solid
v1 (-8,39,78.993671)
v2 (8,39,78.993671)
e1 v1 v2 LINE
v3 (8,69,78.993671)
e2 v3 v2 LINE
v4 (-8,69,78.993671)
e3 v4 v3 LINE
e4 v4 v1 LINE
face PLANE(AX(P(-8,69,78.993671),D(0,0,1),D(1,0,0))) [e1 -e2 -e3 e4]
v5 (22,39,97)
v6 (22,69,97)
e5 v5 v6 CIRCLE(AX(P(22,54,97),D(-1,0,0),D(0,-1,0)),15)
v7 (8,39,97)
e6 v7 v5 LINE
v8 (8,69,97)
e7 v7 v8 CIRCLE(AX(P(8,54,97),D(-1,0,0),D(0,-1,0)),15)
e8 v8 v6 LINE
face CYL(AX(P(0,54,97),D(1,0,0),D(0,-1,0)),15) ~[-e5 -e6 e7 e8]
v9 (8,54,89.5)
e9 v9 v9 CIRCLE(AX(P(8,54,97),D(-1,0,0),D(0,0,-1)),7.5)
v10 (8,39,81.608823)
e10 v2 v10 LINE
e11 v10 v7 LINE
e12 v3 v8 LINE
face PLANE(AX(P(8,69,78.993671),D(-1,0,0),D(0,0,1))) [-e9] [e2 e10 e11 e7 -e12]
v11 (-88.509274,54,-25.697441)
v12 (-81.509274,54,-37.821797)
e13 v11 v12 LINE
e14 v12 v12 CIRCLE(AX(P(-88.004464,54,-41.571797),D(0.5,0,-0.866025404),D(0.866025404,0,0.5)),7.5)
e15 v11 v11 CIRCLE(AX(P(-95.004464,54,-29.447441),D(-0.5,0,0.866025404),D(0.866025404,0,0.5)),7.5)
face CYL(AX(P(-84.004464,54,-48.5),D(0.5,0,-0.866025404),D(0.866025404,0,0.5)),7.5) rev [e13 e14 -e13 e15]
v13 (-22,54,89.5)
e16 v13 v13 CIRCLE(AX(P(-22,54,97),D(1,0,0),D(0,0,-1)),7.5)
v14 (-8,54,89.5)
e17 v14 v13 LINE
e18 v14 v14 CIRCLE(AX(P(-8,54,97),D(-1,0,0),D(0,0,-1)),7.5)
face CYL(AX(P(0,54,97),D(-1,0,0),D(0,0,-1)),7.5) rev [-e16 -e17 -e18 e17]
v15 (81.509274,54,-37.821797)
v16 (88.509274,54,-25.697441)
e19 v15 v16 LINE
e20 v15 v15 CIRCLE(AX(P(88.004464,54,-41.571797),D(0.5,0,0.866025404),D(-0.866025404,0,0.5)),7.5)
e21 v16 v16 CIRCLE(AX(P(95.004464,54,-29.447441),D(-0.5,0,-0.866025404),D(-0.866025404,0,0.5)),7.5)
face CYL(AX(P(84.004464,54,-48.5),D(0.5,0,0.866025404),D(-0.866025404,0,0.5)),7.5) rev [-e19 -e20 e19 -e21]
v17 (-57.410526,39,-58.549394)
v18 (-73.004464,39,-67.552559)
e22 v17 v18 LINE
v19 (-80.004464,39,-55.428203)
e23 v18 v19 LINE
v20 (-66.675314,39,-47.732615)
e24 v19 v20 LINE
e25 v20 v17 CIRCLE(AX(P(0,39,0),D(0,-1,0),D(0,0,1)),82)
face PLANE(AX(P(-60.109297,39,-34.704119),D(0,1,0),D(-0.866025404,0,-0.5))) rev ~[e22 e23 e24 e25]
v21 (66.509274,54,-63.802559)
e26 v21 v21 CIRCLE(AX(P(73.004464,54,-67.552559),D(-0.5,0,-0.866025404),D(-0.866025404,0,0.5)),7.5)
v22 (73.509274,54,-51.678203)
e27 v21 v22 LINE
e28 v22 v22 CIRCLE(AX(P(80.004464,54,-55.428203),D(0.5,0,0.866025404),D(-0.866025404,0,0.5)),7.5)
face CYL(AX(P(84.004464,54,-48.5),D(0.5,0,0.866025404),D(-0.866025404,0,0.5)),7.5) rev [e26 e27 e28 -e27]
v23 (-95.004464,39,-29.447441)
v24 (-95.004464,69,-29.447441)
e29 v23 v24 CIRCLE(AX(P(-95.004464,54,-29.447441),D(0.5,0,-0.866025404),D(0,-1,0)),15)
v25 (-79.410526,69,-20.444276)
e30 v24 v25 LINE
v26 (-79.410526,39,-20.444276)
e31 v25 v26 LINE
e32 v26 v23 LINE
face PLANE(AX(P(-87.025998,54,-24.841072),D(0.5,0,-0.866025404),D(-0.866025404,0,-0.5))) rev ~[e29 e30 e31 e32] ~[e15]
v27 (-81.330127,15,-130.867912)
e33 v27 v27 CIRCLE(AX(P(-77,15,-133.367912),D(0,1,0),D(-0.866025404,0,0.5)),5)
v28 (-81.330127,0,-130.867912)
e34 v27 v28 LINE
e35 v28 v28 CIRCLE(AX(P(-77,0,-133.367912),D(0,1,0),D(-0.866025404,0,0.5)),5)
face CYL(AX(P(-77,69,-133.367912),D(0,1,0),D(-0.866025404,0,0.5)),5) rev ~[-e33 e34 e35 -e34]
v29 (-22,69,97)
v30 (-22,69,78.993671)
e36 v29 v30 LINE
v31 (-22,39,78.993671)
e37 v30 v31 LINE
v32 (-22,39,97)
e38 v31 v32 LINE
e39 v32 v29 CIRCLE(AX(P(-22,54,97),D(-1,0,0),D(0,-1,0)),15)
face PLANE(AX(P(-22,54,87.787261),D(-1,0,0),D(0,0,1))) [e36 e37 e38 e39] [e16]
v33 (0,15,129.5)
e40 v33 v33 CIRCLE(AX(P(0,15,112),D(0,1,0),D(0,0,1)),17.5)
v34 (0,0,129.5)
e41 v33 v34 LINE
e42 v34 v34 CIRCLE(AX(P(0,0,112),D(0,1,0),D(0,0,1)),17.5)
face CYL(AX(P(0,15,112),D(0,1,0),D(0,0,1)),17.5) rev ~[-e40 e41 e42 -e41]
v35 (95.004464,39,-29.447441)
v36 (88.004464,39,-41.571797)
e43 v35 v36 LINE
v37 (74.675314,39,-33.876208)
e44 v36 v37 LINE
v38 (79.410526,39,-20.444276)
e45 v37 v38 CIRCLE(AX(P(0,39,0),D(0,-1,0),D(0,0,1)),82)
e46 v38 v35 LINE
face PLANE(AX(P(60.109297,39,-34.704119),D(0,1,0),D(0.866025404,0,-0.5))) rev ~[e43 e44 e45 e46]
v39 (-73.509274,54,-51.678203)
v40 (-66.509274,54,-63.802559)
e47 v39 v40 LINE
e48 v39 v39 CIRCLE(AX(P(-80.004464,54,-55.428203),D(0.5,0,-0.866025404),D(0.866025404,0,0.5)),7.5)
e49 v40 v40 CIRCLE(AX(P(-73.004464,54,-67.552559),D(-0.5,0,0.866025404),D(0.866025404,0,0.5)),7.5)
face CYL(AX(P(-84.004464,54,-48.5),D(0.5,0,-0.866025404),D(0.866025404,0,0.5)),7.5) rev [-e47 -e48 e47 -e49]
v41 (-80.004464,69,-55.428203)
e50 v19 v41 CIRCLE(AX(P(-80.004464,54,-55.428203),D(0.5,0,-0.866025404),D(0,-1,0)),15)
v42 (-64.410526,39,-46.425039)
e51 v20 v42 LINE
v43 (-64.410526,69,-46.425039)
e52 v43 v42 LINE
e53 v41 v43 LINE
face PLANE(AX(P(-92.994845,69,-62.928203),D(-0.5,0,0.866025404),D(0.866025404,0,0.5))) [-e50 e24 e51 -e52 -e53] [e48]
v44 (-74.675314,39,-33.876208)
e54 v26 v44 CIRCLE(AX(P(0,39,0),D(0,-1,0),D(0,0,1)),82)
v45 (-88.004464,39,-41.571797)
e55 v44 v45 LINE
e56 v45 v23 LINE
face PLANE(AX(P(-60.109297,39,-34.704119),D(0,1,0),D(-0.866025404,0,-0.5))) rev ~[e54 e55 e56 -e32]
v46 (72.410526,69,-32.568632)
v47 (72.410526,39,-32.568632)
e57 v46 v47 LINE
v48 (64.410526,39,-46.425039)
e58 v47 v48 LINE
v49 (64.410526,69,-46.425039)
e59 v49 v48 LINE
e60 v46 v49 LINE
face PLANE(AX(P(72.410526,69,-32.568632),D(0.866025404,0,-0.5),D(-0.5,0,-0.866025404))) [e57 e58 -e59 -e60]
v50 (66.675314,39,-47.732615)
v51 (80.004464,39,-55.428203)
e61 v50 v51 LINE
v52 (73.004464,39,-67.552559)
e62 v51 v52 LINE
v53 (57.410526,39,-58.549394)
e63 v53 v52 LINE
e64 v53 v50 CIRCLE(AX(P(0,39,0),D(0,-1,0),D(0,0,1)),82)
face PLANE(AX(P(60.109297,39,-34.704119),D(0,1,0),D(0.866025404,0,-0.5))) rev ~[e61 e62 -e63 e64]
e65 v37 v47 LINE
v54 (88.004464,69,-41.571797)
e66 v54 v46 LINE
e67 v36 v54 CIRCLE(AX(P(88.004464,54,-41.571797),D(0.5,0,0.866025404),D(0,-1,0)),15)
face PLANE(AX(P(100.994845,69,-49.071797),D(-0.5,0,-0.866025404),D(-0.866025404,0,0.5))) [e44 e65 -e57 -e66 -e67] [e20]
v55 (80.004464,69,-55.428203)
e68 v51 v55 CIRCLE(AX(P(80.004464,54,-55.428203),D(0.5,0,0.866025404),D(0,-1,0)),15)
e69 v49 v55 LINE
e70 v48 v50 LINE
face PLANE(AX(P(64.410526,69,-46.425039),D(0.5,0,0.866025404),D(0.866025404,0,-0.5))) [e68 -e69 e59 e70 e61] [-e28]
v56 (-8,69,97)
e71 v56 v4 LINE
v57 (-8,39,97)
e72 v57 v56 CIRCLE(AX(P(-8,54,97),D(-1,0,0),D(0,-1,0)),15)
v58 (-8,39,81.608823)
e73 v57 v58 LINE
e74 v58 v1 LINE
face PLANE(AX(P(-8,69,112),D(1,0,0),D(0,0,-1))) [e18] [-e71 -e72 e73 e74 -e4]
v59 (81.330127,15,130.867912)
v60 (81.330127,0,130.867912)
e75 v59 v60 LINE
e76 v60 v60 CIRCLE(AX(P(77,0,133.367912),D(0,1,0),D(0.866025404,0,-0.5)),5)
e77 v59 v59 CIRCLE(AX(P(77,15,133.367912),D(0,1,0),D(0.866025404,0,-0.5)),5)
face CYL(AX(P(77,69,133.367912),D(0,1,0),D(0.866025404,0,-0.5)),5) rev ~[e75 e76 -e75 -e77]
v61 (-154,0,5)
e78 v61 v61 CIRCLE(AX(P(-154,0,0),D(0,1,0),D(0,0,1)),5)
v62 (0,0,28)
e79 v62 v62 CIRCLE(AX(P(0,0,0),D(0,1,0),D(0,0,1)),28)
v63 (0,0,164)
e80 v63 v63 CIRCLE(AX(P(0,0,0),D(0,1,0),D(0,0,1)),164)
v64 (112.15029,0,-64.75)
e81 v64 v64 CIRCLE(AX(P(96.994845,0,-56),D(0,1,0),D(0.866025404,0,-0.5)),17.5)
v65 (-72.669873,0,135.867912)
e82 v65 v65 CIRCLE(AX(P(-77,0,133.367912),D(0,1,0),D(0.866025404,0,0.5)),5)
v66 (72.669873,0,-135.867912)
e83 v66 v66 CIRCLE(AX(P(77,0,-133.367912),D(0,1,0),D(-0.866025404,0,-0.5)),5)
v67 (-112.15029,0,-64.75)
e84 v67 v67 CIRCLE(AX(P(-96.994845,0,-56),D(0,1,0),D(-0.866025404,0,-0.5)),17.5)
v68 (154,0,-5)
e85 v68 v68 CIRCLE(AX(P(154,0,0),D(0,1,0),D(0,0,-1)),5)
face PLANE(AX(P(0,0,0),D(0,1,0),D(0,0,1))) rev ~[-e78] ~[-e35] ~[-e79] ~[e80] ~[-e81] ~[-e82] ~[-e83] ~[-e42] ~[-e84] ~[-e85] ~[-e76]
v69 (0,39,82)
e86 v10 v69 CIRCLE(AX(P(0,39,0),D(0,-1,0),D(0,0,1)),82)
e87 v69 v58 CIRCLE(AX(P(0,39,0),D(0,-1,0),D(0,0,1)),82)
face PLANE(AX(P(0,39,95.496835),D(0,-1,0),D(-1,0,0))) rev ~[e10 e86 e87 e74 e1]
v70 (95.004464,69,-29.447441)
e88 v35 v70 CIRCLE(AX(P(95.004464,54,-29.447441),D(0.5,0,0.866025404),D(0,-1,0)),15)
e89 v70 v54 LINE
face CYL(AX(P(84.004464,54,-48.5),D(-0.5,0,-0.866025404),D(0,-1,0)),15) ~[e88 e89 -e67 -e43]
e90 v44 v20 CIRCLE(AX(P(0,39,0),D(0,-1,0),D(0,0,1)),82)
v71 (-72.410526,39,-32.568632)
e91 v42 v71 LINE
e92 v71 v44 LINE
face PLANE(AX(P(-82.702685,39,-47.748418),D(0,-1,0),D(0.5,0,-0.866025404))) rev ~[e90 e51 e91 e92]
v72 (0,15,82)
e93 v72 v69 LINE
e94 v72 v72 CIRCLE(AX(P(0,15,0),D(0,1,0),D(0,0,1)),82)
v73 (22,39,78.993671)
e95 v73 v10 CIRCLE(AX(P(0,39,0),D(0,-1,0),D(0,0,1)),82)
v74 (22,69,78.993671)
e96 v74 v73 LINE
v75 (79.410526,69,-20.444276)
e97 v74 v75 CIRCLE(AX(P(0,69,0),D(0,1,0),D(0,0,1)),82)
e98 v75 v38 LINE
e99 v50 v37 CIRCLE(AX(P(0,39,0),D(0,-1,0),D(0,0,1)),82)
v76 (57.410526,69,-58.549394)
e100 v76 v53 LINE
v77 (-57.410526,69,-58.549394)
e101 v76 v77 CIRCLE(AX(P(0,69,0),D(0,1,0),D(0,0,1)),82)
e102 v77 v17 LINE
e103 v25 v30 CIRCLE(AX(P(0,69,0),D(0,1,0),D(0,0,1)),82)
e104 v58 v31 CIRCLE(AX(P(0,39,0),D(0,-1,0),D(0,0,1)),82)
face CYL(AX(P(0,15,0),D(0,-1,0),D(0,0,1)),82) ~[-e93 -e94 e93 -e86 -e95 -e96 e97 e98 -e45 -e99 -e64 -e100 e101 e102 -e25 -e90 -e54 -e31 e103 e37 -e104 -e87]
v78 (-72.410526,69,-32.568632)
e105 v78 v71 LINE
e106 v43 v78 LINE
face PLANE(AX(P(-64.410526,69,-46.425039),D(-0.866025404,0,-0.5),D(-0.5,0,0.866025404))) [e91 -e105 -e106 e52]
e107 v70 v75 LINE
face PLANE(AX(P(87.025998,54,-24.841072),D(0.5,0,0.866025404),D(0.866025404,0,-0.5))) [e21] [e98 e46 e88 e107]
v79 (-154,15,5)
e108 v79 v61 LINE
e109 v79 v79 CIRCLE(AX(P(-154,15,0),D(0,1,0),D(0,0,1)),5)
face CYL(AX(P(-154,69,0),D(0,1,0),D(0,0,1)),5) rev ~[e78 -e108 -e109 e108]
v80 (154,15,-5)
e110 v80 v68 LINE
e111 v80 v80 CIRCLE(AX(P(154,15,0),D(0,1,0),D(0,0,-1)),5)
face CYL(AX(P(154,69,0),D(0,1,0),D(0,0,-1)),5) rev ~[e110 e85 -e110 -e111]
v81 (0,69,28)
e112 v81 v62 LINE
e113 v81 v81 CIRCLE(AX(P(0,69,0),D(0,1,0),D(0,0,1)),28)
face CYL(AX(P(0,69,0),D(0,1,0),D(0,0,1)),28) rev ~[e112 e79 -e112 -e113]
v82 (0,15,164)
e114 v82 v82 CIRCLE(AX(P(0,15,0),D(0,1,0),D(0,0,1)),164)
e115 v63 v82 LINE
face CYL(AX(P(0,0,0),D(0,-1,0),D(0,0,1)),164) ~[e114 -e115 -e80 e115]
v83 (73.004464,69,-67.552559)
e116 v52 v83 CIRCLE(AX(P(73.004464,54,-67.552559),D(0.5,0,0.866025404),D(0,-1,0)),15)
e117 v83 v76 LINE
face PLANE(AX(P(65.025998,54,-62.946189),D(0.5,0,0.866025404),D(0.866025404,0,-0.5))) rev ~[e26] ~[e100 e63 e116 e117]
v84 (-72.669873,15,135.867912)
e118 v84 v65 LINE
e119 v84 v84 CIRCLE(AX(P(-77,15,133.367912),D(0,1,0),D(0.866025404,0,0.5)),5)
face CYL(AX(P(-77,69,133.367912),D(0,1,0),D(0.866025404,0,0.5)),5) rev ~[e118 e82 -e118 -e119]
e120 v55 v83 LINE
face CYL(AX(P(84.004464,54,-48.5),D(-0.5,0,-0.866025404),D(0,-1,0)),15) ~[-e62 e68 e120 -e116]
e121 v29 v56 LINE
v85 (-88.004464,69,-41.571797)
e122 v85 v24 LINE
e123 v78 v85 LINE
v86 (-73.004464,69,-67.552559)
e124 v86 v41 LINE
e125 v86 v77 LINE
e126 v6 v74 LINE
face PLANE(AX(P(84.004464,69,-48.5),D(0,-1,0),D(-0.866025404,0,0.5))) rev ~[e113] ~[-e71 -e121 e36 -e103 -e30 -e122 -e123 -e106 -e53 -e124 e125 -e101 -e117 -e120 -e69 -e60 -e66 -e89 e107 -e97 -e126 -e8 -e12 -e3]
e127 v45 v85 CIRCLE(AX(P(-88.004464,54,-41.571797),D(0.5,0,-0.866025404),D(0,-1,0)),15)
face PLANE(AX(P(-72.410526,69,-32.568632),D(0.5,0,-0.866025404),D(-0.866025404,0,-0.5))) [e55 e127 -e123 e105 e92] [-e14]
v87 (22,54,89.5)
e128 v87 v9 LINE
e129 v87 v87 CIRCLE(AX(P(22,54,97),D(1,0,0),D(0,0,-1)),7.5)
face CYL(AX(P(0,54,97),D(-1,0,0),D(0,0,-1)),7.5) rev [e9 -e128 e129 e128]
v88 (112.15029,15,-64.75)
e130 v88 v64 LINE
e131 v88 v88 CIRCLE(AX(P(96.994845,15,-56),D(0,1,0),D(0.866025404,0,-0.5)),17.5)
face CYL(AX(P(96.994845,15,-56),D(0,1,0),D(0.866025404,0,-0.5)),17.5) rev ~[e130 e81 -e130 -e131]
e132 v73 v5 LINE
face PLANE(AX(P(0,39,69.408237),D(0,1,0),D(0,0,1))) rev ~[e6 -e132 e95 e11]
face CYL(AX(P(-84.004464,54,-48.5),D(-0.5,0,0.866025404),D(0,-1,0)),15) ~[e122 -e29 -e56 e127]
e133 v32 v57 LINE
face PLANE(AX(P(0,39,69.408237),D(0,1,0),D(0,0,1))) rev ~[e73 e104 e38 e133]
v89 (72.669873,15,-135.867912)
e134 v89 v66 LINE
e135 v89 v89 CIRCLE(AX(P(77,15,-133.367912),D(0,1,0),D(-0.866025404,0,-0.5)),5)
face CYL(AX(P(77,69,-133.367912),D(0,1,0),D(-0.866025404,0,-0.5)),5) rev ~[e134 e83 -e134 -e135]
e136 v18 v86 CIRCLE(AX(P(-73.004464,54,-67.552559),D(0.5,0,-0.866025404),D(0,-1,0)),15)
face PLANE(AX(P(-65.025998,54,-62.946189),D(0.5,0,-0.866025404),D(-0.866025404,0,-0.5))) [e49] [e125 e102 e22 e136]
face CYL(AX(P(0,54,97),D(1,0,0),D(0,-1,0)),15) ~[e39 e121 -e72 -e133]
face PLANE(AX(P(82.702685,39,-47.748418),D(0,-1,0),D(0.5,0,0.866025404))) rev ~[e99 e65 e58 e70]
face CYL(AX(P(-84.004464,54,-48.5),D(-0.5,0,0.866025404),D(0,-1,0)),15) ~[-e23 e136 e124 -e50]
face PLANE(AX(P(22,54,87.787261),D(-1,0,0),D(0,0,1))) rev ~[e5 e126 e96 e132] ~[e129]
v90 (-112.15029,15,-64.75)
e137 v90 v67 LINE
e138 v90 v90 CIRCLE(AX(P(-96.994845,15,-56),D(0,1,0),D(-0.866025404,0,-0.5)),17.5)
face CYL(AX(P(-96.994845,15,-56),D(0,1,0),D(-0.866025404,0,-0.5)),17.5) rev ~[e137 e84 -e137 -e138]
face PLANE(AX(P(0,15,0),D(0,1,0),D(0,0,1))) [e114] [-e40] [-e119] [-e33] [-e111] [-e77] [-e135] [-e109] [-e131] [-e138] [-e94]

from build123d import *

# Parameters (mm, degrees)
BASE_DISC_SKETCH_328_R            = 164
BASE_DISC_328X15_DEPTH            = 15
HUB_SKETCH_164_R                  = 82
HUB_164X54_DEPTH                  = 54
CENTRE_BORE_SKETCH_56_R           = 28
CENTRE_BORE_56_DEPTH              = 242.97727166
CLEVIS_LUG_PROFILE_SKETCH_R       = 7.5
CLEVIS_LUG_DEPTH                  = 22
CLEVIS_SLOT_30_DEPTH              = 30
CLEVIS_LUG_PATTERN_3X_COUNT       = 3
LARGE_HOLE_SKETCH_35_R            = 17.5
LARGE_HOLE_35_DEPTH               = 239.134415824
LARGE_HOLE_PATTERN_3X_35_COUNT    = 3
MOUNTING_HOLE_SKETCH_10_R         = 5
MOUNTING_HOLE_10_DEPTH            = 242.97727166
MOUNTING_HOLE_PATTERN_6X_10_COUNT = 6


with BuildPart() as part:
    # Base Disc Sketch Ø328 → Base Disc Ø328x15 (new body)
    with BuildSketch(Plane(origin=(0, 0, 0), x_dir=(1, 0, 0), z_dir=(0, 1, 0))):
        with Locations(Location((0, 0, 0), (0, 0, 270))):
            Circle(BASE_DISC_SKETCH_328_R)
    extrude(amount=BASE_DISC_328X15_DEPTH)

    # Hub Sketch Ø164 → Hub Ø164x54 (add)
    with BuildSketch(Plane(origin=(0, 15, 0), x_dir=(1, 0, 0), z_dir=(0, 1, 0))):
        with Locations(Location((0, 0, 0), (0, 0, 270))):
            Circle(HUB_SKETCH_164_R)
    extrude(amount=HUB_164X54_DEPTH)

    # Centre Bore Sketch Ø56 → Centre Bore Ø56 (cut, through all)
    with BuildSketch(Plane(origin=(0, 69, 0), x_dir=(1, 0, 0), z_dir=(0, 1, 0))):
        with Locations(Location((0, 0, 0), (0, 0, 270))):
            Circle(CENTRE_BORE_SKETCH_56_R)
    extrude(amount=-CENTRE_BORE_56_DEPTH, mode=Mode.SUBTRACT)

    # Clevis Lug Profile Sketch → Clevis Lug (add, symmetric)
    with BuildSketch(Plane(origin=(0, 0, 0), x_dir=(0, 0, -1), z_dir=(1, 0, 0))):
        with BuildLine():
            Line((-97, 69), (-69.408237338, 69))
            Line((-69.408237338, 69), (-69.408237338, 39))
            Line((-69.408237338, 39), (-97, 39))
            ThreePointArc((-97, 39), (-112, 54), (-97, 69))
        make_face()
        with Locations((-97, 54)):
            Circle(CLEVIS_LUG_PROFILE_SKETCH_R, mode=Mode.SUBTRACT)
    clevis_lug = extrude(amount=CLEVIS_LUG_DEPTH, both=True)

    # Clevis Slot Profile Sketch → Clevis Slot 30 (cut)
    with BuildSketch(Plane(origin=(0, 69, 0), x_dir=(1, 0, 0), z_dir=(0, 1, 0))):
        Polygon((0, -112), (-8, -112), (-8, -78.993670633), (8, -78.993670633), (8, -112), align=None)
    clevis_slot_30 = extrude(amount=-CLEVIS_SLOT_30_DEPTH, mode=Mode.SUBTRACT)

    # Clevis Lug Pattern 3x: Clevis Lug, Clevis Slot 30 ×3 about axis
    clevis_lug_pattern_3x_axis = Axis((0, 0, 0), (0, 1, 0))
    add([clevis_lug.rotate(clevis_lug_pattern_3x_axis, i * 360 / CLEVIS_LUG_PATTERN_3X_COUNT) for i in range(1, CLEVIS_LUG_PATTERN_3X_COUNT)])
    add([clevis_slot_30.rotate(clevis_lug_pattern_3x_axis, i * 360 / CLEVIS_LUG_PATTERN_3X_COUNT) for i in range(1, CLEVIS_LUG_PATTERN_3X_COUNT)], mode=Mode.SUBTRACT)

    # Large Hole Sketch Ø35 → Large Hole Ø35 (cut, through all)
    with BuildSketch(Plane(origin=(0, 15, 0), x_dir=(1, 0, 0), z_dir=(0, 1, 0))):
        with Locations(Location((0, -112, 0), (0, 0, 270))):
            Circle(LARGE_HOLE_SKETCH_35_R)
    large_hole_35 = extrude(amount=-LARGE_HOLE_35_DEPTH, mode=Mode.SUBTRACT)

    # Large Hole Pattern 3xØ35: Large Hole Ø35 ×3 about axis
    large_hole_pattern_3x_35_axis = Axis((0, 0, 0), (0, 1, 0))
    for i in range(1, LARGE_HOLE_PATTERN_3X_35_COUNT):
        add(large_hole_35.rotate(large_hole_pattern_3x_35_axis, i * 360 / LARGE_HOLE_PATTERN_3X_35_COUNT), mode=Mode.SUBTRACT)

    # Mounting Hole Sketch Ø10 → Mounting Hole Ø10 (cut, through all)
    with BuildSketch(Plane(origin=(0, 69, 0), x_dir=(1, 0, 0), z_dir=(0, 1, 0))):
        with Locations(Location((-154, 0, 0), (0, 0, 270))):
            Circle(MOUNTING_HOLE_SKETCH_10_R)
    mounting_hole_10 = extrude(amount=-MOUNTING_HOLE_10_DEPTH, mode=Mode.SUBTRACT)

    # Mounting Hole Pattern 6xØ10: Mounting Hole Ø10 ×6 about axis
    mounting_hole_pattern_6x_10_axis = Axis((0, 0, 0), (0, 1, 0))
    for i in range(1, MOUNTING_HOLE_PATTERN_6X_10_COUNT):
        add(mounting_hole_10.rotate(mounting_hole_pattern_6x_10_axis, i * 360 / MOUNTING_HOLE_PATTERN_6X_10_COUNT), mode=Mode.SUBTRACT)


solid = part.part
